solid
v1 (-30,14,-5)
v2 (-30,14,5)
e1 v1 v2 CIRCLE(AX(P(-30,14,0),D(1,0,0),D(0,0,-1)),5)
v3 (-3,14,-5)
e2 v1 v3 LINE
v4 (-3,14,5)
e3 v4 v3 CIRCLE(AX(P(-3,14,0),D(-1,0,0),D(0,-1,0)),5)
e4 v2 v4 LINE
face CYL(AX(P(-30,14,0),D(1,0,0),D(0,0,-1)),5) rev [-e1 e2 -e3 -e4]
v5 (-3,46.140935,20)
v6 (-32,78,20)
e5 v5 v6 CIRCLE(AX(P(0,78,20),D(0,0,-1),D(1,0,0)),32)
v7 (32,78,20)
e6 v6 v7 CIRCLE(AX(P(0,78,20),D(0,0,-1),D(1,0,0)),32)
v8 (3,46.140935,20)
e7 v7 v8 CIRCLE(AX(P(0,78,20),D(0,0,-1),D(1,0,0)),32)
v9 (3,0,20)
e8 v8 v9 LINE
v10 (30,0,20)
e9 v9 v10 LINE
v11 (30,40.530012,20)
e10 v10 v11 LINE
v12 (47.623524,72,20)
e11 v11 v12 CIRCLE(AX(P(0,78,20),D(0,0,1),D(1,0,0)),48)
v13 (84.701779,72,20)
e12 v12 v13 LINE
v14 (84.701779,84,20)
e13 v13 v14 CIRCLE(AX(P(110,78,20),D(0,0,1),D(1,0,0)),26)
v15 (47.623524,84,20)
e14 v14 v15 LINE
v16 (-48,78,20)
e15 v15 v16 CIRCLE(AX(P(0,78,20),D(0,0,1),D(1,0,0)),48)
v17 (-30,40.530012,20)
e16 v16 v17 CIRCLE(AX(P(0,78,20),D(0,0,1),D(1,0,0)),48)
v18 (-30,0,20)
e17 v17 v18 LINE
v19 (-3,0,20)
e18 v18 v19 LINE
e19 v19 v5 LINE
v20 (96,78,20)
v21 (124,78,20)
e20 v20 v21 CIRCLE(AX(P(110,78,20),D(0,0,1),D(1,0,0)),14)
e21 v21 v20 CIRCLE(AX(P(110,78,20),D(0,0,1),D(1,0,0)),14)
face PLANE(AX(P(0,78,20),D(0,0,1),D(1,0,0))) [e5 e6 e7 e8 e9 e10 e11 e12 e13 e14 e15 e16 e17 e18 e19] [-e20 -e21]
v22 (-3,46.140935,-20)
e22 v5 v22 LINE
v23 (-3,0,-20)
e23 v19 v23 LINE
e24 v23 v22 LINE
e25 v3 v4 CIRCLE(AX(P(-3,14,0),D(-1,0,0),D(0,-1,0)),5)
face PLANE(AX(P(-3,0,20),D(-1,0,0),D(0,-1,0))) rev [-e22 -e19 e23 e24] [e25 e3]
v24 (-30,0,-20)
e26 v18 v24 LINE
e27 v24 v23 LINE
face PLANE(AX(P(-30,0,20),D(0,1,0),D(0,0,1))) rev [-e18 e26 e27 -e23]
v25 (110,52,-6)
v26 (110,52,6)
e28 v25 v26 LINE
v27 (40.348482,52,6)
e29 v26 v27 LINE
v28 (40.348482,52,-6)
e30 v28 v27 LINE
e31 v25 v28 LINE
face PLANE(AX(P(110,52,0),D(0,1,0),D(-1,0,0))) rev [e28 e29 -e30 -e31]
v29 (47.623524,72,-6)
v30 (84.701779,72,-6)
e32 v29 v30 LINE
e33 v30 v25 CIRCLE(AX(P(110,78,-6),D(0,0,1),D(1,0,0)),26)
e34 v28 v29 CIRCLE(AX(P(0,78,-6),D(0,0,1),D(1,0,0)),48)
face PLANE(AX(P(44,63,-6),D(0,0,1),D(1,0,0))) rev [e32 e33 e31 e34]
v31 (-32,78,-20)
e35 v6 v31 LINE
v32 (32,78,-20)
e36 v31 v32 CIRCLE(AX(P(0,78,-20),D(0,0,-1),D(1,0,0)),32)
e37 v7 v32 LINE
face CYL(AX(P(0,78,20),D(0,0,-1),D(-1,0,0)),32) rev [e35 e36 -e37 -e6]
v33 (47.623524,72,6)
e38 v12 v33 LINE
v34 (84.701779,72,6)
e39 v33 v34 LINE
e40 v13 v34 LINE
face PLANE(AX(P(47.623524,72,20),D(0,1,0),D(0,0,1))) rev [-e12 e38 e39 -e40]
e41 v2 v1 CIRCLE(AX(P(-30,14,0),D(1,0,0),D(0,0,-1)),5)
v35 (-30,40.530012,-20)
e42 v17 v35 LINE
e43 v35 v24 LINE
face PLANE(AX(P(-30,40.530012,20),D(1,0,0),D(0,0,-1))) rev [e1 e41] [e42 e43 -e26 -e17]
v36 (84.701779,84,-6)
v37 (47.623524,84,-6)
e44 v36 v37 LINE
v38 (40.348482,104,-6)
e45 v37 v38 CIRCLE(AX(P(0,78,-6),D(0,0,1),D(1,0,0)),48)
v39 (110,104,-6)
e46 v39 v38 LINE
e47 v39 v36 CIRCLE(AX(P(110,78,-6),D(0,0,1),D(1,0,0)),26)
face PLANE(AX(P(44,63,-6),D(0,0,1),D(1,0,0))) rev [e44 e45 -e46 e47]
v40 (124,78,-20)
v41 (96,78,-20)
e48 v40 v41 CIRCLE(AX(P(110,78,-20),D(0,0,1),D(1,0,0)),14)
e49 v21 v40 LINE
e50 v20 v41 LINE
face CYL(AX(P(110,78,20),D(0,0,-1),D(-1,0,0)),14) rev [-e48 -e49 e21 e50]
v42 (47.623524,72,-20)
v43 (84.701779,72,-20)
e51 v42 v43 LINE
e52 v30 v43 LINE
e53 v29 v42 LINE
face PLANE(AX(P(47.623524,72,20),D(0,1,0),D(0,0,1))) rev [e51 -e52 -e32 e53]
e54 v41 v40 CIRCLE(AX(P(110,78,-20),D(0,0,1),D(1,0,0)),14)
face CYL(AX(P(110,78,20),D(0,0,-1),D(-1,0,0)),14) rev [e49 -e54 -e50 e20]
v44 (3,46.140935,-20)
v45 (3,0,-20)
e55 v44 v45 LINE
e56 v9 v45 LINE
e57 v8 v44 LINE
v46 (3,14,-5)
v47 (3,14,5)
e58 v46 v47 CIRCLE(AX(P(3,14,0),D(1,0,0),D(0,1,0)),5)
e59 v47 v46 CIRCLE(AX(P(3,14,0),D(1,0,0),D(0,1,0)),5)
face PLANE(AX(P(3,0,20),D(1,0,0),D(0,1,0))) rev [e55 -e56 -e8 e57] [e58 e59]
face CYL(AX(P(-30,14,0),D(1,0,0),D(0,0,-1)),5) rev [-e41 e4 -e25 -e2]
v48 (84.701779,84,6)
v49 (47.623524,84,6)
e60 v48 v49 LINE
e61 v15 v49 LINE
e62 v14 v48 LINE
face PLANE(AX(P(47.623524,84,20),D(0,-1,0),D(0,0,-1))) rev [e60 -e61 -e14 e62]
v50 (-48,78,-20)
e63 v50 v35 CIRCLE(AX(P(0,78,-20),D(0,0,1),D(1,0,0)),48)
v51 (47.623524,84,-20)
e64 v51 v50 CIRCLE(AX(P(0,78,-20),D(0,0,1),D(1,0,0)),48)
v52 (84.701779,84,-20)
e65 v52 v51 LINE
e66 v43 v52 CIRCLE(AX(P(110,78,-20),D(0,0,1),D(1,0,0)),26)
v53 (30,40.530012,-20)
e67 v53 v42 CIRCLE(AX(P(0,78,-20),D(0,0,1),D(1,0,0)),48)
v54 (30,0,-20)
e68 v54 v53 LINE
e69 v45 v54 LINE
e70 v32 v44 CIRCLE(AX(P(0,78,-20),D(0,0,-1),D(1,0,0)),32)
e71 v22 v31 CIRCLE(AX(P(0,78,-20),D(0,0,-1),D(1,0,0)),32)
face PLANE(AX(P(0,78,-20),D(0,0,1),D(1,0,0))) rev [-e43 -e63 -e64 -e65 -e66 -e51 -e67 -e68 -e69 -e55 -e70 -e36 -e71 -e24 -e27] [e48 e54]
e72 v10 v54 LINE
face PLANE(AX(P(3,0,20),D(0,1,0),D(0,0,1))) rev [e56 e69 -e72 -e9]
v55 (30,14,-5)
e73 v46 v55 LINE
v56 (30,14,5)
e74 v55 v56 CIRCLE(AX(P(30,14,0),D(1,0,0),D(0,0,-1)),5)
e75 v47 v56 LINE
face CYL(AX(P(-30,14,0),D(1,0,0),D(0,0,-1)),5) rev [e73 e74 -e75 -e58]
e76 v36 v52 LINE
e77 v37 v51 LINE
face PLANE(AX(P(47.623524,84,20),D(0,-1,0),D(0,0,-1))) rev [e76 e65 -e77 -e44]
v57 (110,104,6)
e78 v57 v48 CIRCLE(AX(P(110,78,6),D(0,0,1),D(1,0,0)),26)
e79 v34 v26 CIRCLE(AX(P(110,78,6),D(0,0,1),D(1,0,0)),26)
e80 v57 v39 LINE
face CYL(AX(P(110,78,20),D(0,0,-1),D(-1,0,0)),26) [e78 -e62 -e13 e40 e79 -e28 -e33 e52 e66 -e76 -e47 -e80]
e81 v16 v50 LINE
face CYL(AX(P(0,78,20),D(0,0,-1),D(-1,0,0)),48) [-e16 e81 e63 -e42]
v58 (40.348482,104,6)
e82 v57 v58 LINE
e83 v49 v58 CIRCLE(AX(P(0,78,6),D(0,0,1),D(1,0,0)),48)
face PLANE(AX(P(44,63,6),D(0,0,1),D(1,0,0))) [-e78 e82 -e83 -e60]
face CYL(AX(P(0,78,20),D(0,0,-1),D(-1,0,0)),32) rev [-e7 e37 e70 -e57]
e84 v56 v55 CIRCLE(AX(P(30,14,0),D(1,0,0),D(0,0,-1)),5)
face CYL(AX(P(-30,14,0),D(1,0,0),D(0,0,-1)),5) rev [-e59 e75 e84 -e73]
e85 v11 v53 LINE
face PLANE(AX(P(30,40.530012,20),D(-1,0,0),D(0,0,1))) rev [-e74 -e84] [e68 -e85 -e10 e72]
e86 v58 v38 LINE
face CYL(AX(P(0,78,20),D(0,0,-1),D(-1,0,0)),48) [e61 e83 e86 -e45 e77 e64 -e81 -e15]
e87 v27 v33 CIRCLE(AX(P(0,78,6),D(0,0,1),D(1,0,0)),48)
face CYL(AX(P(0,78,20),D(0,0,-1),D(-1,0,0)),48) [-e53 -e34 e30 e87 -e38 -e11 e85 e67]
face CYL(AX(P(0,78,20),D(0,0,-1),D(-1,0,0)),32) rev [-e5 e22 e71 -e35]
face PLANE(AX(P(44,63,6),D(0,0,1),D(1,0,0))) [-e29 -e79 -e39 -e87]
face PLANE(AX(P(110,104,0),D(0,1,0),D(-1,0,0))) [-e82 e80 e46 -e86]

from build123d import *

# Parameters (mm, degrees)
CLAMP_EYE_96X40_DEPTH       = 20
ARM_AND_SMALL_EYE_PROFILE_R = 14
ARM_AND_SMALL_EYE_DEPTH     = 20
CLAMP_SCREW_HOLE_SKETCH_R   = 5
CLAMP_SCREW_HOLE_DEPTH      = 60
ARM_RIB_1_REACH             = 188.473
ARM_RIB_1_SKETCH_WALL_W     = 444.596554162
ARM_RIB_1_SKETCH_WALL_H     = 12
ARM_RIB_2_REACH             = 188.473
ARM_RIB_2_SKETCH_WALL_W     = 444.596554162
ARM_RIB_2_SKETCH_WALL_H     = 12


with BuildPart() as part:
    # Clamp Eye Profile → Clamp Eye Ø96x40 (new, symmetric)
    with BuildSketch(Plane.XY):
        with BuildLine():
            Line((-30, 40.53001201), (-30, 0))
            Line((-30, 0), (-3, 0))
            Line((-3, 0), (-3, 46.140935356))
            ThreePointArc((-3, 46.140935356), (0, 110), (3, 46.140935356))
            Line((3, 46.140935356), (3, 0))
            Line((3, 0), (30, 0))
            Line((30, 0), (30, 40.53001201))
            ThreePointArc((30, 40.53001201), (0, 126), (-30, 40.53001201))
        make_face()
    extrude(amount=CLAMP_EYE_96X40_DEPTH, both=True)

    # Arm and Small Eye Profile → Arm and Small Eye (add, symmetric)
    with BuildSketch(Plane.XY):
        with BuildLine():
            Line((47.623523599, 72), (84.701778719, 72))
            ThreePointArc((84.701778719, 72), (136, 78), (84.701778719, 84))
            Line((84.701778719, 84), (47.623523599, 84))
            ThreePointArc((47.623523599, 84), (48, 78), (47.623523599, 72))
        make_face()
        with Locations((110, 78)):
            Circle(ARM_AND_SMALL_EYE_PROFILE_R, mode=Mode.SUBTRACT)
    extrude(amount=ARM_AND_SMALL_EYE_DEPTH, both=True)

    # Clamp Screw Hole Sketch → Clamp Screw Hole (cut)
    with BuildSketch(Plane(origin=(30, 0, 0), x_dir=(0, 0, -1), z_dir=(1, 0, 0))):
        with Locations((0, 14)):
            Circle(CLAMP_SCREW_HOLE_SKETCH_R)
    extrude(amount=-CLAMP_SCREW_HOLE_DEPTH, mode=Mode.SUBTRACT)

    # Arm Rib 1 Sketch wall → Arm Rib 1 (add, up to next)
    with BuildSketch(Plane(origin=(75.174241002, 104, 0), x_dir=(-1, 0, 0), z_dir=(0, -1, 0)), mode=Mode.PRIVATE) as arm_rib_1_sk1:
        Rectangle(ARM_RIB_1_SKETCH_WALL_W, ARM_RIB_1_SKETCH_WALL_H)
    arm_rib_1_tool1 = extrude(arm_rib_1_sk1.sketch, amount=ARM_RIB_1_REACH, mode=Mode.PRIVATE) - part.part
    add(arm_rib_1_tool1.solids().sort_by_distance((75.174241002, 104, 0))[0])

    # Arm Rib 2 Sketch wall → Arm Rib 2 (add, up to next)
    with BuildSketch(Plane(origin=(75.174241002, 52, 0), x_dir=(-1, 0, 0), z_dir=(0, -1, 0)), mode=Mode.PRIVATE) as arm_rib_2_sk1:
        Rectangle(ARM_RIB_2_SKETCH_WALL_W, ARM_RIB_2_SKETCH_WALL_H)
    arm_rib_2_tool1 = extrude(arm_rib_2_sk1.sketch, amount=-ARM_RIB_2_REACH, mode=Mode.PRIVATE) - part.part
    add(arm_rib_2_tool1.solids().sort_by_distance((75.174241002, 52, 0))[0])


solid = part.part
